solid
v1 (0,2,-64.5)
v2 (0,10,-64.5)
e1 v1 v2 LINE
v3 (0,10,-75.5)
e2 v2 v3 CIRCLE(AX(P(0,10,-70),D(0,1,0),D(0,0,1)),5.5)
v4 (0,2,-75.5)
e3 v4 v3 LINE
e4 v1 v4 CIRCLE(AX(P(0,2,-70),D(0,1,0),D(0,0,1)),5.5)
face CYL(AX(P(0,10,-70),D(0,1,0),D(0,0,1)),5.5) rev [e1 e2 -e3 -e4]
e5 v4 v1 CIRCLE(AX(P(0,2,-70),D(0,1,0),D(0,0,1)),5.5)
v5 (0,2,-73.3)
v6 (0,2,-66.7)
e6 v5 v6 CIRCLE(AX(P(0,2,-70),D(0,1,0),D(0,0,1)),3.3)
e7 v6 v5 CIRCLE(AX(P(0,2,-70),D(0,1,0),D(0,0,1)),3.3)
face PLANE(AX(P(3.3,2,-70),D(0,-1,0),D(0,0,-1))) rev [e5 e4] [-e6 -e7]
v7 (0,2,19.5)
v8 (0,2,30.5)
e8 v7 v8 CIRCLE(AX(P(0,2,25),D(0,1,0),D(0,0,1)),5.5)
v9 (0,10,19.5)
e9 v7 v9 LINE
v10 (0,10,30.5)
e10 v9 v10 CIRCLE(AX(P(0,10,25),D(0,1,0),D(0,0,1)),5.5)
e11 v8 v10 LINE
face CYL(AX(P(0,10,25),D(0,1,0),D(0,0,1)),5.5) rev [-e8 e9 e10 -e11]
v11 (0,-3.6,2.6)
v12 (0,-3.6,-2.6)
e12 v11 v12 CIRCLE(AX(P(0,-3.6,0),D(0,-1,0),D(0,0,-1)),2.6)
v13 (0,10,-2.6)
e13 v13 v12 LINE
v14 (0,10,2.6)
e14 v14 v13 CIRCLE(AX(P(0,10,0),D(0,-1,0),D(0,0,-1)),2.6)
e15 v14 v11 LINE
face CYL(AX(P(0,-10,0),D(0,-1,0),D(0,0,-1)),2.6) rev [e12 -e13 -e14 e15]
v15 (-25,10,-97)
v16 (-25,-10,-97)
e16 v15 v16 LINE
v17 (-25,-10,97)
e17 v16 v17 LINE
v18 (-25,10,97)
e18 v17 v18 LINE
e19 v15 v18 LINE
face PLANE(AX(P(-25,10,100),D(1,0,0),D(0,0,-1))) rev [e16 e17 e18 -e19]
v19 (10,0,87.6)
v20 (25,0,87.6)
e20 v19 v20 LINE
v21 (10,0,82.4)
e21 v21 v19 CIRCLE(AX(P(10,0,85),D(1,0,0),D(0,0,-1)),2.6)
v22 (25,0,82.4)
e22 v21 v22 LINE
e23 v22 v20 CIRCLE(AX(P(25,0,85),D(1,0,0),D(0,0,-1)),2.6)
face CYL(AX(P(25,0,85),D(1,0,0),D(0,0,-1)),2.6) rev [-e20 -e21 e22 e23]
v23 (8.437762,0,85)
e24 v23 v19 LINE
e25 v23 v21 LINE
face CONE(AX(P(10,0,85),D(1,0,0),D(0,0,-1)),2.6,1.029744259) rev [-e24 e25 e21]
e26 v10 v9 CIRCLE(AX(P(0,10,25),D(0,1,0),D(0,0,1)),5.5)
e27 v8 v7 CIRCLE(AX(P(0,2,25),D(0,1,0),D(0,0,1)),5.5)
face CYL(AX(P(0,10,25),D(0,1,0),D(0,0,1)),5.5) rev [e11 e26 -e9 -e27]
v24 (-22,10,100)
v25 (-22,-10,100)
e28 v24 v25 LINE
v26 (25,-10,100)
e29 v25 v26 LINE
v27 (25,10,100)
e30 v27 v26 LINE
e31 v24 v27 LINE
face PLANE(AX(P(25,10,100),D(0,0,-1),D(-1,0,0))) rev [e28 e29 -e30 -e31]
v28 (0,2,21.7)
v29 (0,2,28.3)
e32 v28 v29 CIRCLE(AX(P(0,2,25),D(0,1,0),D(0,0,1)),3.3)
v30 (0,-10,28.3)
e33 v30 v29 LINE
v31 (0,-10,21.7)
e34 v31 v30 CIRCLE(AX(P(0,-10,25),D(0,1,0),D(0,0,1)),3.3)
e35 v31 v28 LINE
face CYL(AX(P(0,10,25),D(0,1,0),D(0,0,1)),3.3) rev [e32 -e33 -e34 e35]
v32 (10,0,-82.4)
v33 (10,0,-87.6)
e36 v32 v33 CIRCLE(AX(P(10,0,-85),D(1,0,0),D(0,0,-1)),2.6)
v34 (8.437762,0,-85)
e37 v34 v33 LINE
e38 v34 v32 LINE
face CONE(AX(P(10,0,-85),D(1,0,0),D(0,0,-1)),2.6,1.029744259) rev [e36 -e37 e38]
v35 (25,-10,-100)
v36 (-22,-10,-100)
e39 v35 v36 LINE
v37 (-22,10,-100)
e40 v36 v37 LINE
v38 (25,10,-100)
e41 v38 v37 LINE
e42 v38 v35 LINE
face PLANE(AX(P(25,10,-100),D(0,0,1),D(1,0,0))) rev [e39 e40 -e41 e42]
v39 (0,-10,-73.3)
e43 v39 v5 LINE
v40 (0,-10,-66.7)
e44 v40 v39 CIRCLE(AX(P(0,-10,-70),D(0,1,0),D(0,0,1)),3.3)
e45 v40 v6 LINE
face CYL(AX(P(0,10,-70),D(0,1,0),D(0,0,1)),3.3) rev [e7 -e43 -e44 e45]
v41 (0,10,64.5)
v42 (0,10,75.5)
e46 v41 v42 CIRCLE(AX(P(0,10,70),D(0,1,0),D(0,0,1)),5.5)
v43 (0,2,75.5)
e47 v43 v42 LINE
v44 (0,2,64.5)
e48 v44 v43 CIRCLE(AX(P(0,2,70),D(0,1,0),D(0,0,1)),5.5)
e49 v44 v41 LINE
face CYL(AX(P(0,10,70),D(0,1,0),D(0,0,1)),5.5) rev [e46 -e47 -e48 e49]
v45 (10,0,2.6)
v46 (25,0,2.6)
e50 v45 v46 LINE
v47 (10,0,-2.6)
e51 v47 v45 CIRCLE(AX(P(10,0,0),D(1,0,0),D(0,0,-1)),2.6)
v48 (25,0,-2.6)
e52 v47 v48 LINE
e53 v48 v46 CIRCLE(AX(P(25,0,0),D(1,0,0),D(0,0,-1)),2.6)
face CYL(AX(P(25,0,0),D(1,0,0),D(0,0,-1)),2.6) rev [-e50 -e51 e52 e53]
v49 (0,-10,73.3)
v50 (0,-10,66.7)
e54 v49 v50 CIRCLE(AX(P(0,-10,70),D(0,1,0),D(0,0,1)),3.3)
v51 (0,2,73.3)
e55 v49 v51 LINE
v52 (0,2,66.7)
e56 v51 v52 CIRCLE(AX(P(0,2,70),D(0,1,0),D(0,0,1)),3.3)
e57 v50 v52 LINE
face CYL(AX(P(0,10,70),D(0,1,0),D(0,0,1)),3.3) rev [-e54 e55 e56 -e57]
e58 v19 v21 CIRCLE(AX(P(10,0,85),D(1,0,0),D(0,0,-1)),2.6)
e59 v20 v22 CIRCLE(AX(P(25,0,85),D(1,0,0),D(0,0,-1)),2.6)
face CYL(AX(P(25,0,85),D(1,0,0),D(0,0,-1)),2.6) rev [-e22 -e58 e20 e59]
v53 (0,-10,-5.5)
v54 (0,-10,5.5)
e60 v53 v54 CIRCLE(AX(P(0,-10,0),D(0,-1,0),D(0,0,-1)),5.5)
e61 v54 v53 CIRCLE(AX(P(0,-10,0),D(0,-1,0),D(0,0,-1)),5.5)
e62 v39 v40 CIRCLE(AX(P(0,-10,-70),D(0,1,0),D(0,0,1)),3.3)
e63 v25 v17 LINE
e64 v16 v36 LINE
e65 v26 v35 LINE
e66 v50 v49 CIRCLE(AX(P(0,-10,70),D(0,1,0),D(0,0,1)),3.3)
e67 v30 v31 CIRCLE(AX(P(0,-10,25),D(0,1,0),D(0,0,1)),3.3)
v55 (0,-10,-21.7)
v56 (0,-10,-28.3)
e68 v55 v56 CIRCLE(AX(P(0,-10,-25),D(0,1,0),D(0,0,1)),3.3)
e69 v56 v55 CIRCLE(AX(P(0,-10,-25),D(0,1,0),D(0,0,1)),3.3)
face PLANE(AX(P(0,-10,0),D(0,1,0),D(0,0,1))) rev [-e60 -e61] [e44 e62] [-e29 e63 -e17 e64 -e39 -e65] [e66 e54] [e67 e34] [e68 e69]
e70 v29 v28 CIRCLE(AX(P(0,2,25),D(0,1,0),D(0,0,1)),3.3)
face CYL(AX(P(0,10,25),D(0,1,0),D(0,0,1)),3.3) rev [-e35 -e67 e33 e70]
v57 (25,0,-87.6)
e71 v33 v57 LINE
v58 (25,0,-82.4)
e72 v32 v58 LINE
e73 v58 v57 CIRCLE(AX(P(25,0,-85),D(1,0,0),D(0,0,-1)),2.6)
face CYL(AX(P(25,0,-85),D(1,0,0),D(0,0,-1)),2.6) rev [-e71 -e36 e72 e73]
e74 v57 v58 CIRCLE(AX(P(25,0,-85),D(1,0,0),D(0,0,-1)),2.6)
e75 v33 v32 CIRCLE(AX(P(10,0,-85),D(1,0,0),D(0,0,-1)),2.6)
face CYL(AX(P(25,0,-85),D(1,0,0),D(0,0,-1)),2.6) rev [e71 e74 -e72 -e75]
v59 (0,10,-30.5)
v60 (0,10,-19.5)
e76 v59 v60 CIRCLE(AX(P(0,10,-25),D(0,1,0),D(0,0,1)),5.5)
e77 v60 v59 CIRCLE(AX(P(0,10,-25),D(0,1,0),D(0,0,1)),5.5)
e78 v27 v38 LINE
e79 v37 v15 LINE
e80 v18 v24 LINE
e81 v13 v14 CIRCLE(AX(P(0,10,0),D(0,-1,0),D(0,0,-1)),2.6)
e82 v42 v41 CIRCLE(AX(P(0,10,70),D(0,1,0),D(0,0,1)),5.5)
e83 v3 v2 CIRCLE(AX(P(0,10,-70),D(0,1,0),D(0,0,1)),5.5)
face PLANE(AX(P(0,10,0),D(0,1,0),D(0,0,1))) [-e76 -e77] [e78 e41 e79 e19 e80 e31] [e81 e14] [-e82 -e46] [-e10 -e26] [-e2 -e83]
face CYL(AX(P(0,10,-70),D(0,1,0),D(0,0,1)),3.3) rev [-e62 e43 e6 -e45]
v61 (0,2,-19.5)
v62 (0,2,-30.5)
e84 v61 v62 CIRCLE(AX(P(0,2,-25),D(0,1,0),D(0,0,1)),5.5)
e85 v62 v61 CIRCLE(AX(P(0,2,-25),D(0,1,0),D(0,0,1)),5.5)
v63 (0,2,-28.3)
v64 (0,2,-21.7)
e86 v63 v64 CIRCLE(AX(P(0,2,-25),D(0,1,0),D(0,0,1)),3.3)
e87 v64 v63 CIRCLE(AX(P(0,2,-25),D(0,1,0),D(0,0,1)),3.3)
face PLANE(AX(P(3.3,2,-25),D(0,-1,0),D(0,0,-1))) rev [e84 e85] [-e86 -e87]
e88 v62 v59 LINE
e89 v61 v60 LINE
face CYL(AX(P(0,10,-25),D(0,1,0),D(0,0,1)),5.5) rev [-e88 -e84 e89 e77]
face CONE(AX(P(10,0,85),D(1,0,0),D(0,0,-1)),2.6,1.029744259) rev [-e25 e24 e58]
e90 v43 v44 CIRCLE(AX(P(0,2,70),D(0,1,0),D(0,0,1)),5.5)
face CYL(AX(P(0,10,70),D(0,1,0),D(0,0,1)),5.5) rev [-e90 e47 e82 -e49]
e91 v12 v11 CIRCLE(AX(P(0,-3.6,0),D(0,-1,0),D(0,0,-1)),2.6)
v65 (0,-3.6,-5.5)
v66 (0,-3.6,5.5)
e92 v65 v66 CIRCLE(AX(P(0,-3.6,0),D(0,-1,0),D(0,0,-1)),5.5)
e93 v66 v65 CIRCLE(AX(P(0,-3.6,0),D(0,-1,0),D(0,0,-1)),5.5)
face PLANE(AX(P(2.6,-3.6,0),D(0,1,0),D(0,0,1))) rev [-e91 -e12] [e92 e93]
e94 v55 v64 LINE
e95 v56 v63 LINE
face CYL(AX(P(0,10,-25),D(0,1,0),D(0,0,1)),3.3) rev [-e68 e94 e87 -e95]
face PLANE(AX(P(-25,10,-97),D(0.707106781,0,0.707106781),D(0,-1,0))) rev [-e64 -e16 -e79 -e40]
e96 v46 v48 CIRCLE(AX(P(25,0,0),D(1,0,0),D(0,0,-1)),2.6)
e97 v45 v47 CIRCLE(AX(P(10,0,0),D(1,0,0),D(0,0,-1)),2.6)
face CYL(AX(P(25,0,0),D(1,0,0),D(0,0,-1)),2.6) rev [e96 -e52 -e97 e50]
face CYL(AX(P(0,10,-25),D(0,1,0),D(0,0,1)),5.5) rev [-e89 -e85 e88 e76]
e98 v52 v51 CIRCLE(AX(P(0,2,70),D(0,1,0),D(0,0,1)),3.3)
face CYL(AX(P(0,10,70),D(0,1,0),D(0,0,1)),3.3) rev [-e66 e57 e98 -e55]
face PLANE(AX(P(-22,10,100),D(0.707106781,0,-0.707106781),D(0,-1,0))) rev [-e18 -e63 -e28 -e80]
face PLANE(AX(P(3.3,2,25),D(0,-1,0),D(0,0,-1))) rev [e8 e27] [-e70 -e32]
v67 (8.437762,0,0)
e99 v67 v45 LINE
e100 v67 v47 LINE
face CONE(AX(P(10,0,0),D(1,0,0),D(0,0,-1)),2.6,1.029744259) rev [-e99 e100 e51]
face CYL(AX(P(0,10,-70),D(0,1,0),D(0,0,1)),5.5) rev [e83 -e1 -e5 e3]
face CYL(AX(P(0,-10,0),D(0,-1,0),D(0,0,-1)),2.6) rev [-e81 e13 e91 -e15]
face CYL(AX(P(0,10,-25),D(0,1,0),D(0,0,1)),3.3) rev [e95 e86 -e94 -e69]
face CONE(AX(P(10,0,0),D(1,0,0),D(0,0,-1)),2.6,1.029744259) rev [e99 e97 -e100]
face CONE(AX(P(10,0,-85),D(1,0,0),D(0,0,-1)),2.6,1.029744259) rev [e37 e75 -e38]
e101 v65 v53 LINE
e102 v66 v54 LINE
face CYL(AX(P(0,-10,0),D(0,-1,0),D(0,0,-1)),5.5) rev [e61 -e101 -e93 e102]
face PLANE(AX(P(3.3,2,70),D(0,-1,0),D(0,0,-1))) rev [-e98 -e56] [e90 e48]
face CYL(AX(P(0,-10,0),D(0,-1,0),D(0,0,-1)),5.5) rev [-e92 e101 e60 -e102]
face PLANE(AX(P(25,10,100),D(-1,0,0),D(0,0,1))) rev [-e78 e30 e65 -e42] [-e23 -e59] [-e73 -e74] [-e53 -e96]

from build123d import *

# Parameters (mm, degrees)
SKETCH_1_W                   = 50
SKETCH_1_H                   = 200
EXTRUDE_1_DEPTH              = 10
HOLE_WIZARD_M6_1_D           = 6.6
HOLE_WIZARD_M6_1_CBORE_D     = 11
HOLE_WIZARD_M6_1_CBORE_DEPTH = 8
HOLE_WIZARD_M6_1_2_D         = 5.2
HOLE_WIZARD_M6_1_2_DEPTH     = 15
HOLE_WIZARD_M6_1_2_TIP       = 1.562237609
HOLE_WIZARD_M6_2_D           = 5.2
HOLE_WIZARD_M6_2_CBORE_D     = 11
HOLE_WIZARD_M6_2_CBORE_DEPTH = 6.4
CHAMFER_1_SIZE               = 3


with BuildPart() as part:
    # 草图1 → 凸台-拉伸1 (new, symmetric)
    with BuildSketch(Plane(origin=(0, 0, 0), x_dir=(1, 0, 0), z_dir=(0, 1, 0))):
        Rectangle(SKETCH_1_W, SKETCH_1_H)
    extrude(amount=EXTRUDE_1_DEPTH, both=True)

    # Hole Wizard M6 _1 (through all)
    with Locations(Plane(origin=(0, 10, 0), x_dir=(1, 0, 0), z_dir=(0, 1, 0))):
        with Locations((0, 70), (0, -70), (0, 25), (0, -25)):
            CounterBoreHole(HOLE_WIZARD_M6_1_D / 2, HOLE_WIZARD_M6_1_CBORE_D / 2, HOLE_WIZARD_M6_1_CBORE_DEPTH)

    # Hole Wizard M6 _1 2
    with Locations(Plane(origin=(25, 0, 0), x_dir=(0, 0, -1), z_dir=(1, 0, 0))):
        with Locations((-85, 0), (0, 0), (85, 0)):
            Hole(HOLE_WIZARD_M6_1_2_D / 2, depth=HOLE_WIZARD_M6_1_2_DEPTH)
            with Locations((0, 0, -(HOLE_WIZARD_M6_1_2_DEPTH + HOLE_WIZARD_M6_1_2_TIP / 2))):  # 118° drill point
                Cone(0, HOLE_WIZARD_M6_1_2_D / 2, HOLE_WIZARD_M6_1_2_TIP, mode=Mode.SUBTRACT)

    # M6 六角凹头螺钉的柱形沉头孔2 (through all)
    with Locations(Plane(origin=(0, -10, 0), x_dir=(-1, 0, 0), z_dir=(0, -1, 0))):
        with Locations((0, 0)):
            CounterBoreHole(HOLE_WIZARD_M6_2_D / 2, HOLE_WIZARD_M6_2_CBORE_D / 2, HOLE_WIZARD_M6_2_CBORE_DEPTH)

    # 倒角1
    chamfer_1_edges = [part.edges().sort_by_distance(p)[0] for p in [
        (-25, 0, -100),
        (-25, 0, 100),
    ]]
    chamfer(chamfer_1_edges, length=CHAMFER_1_SIZE)


solid = part.part
